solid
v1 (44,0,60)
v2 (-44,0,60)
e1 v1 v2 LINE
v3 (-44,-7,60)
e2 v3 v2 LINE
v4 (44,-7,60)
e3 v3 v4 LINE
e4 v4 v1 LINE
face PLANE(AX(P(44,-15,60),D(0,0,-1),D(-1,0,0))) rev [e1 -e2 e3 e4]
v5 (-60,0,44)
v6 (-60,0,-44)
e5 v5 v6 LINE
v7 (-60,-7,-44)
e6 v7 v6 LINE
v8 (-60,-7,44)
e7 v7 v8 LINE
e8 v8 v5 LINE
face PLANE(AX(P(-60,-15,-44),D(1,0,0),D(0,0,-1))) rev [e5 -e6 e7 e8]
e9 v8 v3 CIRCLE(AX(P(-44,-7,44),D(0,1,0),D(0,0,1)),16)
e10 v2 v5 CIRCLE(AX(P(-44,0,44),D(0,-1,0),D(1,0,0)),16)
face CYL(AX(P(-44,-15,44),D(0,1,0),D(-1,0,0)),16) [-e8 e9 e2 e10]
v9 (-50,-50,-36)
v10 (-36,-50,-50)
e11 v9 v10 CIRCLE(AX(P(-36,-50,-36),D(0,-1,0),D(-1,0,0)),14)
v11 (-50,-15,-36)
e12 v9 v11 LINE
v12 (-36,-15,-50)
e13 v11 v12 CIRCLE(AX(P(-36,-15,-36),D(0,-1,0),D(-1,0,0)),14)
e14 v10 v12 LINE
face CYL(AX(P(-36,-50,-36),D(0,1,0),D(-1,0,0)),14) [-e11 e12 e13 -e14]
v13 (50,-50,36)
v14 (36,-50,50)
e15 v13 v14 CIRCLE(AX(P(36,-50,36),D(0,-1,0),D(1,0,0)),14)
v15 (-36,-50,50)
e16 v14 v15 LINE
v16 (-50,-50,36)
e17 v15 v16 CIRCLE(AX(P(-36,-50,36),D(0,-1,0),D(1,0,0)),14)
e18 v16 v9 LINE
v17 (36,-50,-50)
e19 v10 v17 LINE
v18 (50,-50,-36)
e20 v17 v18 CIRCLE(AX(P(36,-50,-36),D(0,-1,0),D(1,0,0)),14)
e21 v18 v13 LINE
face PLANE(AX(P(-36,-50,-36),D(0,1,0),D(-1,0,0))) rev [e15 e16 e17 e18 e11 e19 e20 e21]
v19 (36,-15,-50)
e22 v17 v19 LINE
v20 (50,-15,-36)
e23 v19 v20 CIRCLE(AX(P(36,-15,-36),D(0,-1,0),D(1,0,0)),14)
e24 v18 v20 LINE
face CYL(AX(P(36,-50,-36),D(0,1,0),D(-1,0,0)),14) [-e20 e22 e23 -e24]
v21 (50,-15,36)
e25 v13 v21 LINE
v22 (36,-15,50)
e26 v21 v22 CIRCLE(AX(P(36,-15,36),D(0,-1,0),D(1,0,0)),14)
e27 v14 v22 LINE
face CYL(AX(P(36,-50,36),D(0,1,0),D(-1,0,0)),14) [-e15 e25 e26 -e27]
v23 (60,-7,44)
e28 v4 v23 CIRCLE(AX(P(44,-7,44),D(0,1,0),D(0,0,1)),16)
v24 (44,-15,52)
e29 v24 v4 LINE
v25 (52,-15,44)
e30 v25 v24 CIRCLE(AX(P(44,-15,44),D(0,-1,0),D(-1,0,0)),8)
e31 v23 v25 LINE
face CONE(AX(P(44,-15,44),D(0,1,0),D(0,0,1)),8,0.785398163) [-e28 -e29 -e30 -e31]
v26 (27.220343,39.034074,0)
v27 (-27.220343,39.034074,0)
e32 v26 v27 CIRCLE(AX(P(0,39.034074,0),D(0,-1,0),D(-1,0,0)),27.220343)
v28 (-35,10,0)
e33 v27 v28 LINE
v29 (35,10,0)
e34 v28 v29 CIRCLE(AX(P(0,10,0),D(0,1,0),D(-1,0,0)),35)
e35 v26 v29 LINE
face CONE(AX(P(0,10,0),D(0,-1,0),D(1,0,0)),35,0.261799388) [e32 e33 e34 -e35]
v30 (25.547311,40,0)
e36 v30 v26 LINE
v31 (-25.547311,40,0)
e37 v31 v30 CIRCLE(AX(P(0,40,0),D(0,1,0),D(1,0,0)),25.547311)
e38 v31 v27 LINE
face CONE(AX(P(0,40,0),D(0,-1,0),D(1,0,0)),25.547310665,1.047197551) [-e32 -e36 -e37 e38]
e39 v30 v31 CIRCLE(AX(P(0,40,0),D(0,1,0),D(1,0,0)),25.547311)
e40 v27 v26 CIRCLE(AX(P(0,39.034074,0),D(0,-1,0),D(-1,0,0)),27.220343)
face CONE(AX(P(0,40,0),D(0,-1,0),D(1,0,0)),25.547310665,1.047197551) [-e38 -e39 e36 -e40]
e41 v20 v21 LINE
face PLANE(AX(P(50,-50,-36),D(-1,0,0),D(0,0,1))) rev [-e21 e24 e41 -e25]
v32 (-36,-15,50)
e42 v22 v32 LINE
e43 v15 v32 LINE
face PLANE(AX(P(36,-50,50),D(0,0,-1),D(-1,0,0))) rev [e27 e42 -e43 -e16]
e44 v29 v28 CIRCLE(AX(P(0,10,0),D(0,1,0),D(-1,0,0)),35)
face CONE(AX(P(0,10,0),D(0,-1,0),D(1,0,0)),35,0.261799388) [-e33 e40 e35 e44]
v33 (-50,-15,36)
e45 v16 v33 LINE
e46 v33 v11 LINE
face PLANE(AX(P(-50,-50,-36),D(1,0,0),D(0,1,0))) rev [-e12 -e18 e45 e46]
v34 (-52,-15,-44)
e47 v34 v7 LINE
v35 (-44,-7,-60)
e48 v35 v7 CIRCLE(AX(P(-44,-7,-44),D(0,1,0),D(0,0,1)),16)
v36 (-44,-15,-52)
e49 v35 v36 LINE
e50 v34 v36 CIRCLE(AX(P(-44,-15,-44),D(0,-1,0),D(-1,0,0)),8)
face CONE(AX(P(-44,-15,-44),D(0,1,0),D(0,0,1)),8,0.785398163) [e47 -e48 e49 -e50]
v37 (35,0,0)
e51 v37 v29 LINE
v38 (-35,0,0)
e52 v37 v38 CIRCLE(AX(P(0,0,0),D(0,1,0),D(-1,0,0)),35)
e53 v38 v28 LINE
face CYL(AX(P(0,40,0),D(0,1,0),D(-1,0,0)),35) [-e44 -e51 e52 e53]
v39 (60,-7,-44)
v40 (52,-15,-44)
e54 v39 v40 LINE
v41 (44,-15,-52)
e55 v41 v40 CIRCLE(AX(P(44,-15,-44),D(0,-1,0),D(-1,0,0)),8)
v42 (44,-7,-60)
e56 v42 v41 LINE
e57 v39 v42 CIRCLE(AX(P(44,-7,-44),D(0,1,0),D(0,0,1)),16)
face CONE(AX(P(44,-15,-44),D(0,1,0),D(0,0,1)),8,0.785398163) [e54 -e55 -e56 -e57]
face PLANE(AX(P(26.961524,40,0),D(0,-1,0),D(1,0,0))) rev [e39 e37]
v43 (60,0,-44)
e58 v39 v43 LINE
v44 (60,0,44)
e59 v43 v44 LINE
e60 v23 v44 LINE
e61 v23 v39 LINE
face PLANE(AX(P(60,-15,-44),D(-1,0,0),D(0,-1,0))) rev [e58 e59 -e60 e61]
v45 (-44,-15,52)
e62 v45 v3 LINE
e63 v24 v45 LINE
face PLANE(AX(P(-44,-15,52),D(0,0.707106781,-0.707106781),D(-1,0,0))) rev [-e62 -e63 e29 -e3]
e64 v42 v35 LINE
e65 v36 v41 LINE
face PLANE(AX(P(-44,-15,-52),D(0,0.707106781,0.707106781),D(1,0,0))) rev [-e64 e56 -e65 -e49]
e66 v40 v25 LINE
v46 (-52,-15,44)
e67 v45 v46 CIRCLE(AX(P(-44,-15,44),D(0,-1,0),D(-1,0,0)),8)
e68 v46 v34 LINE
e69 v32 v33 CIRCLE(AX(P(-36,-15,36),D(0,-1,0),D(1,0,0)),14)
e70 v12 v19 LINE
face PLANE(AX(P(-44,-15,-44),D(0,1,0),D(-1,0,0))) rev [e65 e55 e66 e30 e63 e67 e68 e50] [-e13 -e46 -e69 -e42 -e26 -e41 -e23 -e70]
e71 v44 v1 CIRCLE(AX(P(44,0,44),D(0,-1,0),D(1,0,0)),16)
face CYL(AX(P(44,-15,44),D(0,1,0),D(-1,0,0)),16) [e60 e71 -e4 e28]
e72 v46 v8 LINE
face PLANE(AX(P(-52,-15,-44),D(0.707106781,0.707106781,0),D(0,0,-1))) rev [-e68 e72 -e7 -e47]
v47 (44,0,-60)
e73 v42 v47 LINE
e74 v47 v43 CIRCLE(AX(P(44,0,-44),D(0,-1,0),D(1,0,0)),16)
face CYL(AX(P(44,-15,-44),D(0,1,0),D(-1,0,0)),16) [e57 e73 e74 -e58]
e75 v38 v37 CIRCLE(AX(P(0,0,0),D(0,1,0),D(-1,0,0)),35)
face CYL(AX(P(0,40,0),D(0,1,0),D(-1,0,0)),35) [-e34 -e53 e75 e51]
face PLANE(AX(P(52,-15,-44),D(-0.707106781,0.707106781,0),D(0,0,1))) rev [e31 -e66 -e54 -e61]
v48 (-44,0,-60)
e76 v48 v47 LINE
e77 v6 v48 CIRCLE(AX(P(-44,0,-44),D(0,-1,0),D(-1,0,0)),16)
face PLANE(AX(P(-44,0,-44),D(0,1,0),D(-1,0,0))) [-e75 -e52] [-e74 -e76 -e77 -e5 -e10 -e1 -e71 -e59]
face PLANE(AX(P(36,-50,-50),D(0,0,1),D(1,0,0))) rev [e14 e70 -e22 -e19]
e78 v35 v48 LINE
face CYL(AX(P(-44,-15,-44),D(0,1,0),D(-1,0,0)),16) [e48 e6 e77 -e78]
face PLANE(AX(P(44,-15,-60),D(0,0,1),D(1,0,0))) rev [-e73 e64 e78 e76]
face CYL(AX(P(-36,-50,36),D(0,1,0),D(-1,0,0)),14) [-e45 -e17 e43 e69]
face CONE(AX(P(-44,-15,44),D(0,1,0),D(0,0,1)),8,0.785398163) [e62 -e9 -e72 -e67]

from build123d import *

# Parameters (mm, degrees)
CHAMFER1_SIZE       = 1
CHAMFER1_SIZE2      = 1.414213562
BOSS_EXTRUDE1_DEPTH = 15
BOSS_EXTRUDE2_DEPTH = 35
CHAMFER2_SIZE       = 8


with BuildPart() as part:
    # Sketch1 → Revolve1 (revolve)
    with BuildSketch(Plane.XY, mode=Mode.PRIVATE) as revolve1_sk:
        Polygon((0, 0), (35, 0), (35, 10), (26.961524227, 40), (0, 40), align=None)
    revolve(revolve1_sk.sketch.rotate(Axis((0, 40, 0), (0, -1, 0)), 180), axis=Axis((0, 40, 0), (0, -1, 0)))

    # Chamfer1
    chamfer1_edges = [part.edges().sort_by_distance(p)[0] for p in [
        (26.961524227, 40, 0),
    ]]
    chamfer1_side = [part.faces().sort_by_distance(p)[0] for p in [
        (30.980762114, 25, 0),
    ]]
    chamfer(chamfer1_edges, length=CHAMFER1_SIZE, length2=CHAMFER1_SIZE2, reference=chamfer1_side[0])

    # Sketch2 → Boss-Extrude1 (add)
    with BuildSketch(Plane.XZ):
        with BuildLine():
            Line((44, -60), (-44, -60))
            ThreePointArc((-44, -60), (-55.313708499, -55.313708499), (-60, -44))
            Line((-60, -44), (-60, 44))
            ThreePointArc((-60, 44), (-55.313708499, 55.313708499), (-44, 60))
            Line((-44, 60), (44, 60))
            ThreePointArc((44, 60), (55.313708499, 55.313708499), (60, 44))
            Line((60, 44), (60, -44))
            ThreePointArc((60, -44), (55.313708499, -55.313708499), (44, -60))
        make_face()
    extrude(amount=BOSS_EXTRUDE1_DEPTH)

    # Sketch3 → Boss-Extrude2 (add)
    with BuildSketch(Plane.XZ.offset(15)):
        with BuildLine():
            Line((36, -50), (-36, -50))
            ThreePointArc((-36, -50), (-45.899494937, -45.899494937), (-50, -36))
            Line((-50, -36), (-50, 36))
            ThreePointArc((-50, 36), (-45.899494937, 45.899494937), (-36, 50))
            Line((-36, 50), (36, 50))
            ThreePointArc((36, 50), (45.899494937, 45.899494937), (50, 36))
            Line((50, 36), (50, -36))
            ThreePointArc((50, -36), (45.899494937, -45.899494937), (36, -50))
        make_face()
    extrude(amount=BOSS_EXTRUDE2_DEPTH)

    # Chamfer2
    chamfer2_edges = [part.edges().sort_by_distance(p)[0] for p in [
        (-55.313708499, -15, -55.313708499),
        (0, -15, -60),
        (55.313708499, -15, -55.313708499),
        (60, -15, 0),
        (55.313708499, -15, 55.313708499),
        (0, -15, 60),
        (-55.313708499, -15, 55.313708499),
        (-60, -15, 0),
    ]]
    chamfer(chamfer2_edges, length=CHAMFER2_SIZE)


solid = part.part
